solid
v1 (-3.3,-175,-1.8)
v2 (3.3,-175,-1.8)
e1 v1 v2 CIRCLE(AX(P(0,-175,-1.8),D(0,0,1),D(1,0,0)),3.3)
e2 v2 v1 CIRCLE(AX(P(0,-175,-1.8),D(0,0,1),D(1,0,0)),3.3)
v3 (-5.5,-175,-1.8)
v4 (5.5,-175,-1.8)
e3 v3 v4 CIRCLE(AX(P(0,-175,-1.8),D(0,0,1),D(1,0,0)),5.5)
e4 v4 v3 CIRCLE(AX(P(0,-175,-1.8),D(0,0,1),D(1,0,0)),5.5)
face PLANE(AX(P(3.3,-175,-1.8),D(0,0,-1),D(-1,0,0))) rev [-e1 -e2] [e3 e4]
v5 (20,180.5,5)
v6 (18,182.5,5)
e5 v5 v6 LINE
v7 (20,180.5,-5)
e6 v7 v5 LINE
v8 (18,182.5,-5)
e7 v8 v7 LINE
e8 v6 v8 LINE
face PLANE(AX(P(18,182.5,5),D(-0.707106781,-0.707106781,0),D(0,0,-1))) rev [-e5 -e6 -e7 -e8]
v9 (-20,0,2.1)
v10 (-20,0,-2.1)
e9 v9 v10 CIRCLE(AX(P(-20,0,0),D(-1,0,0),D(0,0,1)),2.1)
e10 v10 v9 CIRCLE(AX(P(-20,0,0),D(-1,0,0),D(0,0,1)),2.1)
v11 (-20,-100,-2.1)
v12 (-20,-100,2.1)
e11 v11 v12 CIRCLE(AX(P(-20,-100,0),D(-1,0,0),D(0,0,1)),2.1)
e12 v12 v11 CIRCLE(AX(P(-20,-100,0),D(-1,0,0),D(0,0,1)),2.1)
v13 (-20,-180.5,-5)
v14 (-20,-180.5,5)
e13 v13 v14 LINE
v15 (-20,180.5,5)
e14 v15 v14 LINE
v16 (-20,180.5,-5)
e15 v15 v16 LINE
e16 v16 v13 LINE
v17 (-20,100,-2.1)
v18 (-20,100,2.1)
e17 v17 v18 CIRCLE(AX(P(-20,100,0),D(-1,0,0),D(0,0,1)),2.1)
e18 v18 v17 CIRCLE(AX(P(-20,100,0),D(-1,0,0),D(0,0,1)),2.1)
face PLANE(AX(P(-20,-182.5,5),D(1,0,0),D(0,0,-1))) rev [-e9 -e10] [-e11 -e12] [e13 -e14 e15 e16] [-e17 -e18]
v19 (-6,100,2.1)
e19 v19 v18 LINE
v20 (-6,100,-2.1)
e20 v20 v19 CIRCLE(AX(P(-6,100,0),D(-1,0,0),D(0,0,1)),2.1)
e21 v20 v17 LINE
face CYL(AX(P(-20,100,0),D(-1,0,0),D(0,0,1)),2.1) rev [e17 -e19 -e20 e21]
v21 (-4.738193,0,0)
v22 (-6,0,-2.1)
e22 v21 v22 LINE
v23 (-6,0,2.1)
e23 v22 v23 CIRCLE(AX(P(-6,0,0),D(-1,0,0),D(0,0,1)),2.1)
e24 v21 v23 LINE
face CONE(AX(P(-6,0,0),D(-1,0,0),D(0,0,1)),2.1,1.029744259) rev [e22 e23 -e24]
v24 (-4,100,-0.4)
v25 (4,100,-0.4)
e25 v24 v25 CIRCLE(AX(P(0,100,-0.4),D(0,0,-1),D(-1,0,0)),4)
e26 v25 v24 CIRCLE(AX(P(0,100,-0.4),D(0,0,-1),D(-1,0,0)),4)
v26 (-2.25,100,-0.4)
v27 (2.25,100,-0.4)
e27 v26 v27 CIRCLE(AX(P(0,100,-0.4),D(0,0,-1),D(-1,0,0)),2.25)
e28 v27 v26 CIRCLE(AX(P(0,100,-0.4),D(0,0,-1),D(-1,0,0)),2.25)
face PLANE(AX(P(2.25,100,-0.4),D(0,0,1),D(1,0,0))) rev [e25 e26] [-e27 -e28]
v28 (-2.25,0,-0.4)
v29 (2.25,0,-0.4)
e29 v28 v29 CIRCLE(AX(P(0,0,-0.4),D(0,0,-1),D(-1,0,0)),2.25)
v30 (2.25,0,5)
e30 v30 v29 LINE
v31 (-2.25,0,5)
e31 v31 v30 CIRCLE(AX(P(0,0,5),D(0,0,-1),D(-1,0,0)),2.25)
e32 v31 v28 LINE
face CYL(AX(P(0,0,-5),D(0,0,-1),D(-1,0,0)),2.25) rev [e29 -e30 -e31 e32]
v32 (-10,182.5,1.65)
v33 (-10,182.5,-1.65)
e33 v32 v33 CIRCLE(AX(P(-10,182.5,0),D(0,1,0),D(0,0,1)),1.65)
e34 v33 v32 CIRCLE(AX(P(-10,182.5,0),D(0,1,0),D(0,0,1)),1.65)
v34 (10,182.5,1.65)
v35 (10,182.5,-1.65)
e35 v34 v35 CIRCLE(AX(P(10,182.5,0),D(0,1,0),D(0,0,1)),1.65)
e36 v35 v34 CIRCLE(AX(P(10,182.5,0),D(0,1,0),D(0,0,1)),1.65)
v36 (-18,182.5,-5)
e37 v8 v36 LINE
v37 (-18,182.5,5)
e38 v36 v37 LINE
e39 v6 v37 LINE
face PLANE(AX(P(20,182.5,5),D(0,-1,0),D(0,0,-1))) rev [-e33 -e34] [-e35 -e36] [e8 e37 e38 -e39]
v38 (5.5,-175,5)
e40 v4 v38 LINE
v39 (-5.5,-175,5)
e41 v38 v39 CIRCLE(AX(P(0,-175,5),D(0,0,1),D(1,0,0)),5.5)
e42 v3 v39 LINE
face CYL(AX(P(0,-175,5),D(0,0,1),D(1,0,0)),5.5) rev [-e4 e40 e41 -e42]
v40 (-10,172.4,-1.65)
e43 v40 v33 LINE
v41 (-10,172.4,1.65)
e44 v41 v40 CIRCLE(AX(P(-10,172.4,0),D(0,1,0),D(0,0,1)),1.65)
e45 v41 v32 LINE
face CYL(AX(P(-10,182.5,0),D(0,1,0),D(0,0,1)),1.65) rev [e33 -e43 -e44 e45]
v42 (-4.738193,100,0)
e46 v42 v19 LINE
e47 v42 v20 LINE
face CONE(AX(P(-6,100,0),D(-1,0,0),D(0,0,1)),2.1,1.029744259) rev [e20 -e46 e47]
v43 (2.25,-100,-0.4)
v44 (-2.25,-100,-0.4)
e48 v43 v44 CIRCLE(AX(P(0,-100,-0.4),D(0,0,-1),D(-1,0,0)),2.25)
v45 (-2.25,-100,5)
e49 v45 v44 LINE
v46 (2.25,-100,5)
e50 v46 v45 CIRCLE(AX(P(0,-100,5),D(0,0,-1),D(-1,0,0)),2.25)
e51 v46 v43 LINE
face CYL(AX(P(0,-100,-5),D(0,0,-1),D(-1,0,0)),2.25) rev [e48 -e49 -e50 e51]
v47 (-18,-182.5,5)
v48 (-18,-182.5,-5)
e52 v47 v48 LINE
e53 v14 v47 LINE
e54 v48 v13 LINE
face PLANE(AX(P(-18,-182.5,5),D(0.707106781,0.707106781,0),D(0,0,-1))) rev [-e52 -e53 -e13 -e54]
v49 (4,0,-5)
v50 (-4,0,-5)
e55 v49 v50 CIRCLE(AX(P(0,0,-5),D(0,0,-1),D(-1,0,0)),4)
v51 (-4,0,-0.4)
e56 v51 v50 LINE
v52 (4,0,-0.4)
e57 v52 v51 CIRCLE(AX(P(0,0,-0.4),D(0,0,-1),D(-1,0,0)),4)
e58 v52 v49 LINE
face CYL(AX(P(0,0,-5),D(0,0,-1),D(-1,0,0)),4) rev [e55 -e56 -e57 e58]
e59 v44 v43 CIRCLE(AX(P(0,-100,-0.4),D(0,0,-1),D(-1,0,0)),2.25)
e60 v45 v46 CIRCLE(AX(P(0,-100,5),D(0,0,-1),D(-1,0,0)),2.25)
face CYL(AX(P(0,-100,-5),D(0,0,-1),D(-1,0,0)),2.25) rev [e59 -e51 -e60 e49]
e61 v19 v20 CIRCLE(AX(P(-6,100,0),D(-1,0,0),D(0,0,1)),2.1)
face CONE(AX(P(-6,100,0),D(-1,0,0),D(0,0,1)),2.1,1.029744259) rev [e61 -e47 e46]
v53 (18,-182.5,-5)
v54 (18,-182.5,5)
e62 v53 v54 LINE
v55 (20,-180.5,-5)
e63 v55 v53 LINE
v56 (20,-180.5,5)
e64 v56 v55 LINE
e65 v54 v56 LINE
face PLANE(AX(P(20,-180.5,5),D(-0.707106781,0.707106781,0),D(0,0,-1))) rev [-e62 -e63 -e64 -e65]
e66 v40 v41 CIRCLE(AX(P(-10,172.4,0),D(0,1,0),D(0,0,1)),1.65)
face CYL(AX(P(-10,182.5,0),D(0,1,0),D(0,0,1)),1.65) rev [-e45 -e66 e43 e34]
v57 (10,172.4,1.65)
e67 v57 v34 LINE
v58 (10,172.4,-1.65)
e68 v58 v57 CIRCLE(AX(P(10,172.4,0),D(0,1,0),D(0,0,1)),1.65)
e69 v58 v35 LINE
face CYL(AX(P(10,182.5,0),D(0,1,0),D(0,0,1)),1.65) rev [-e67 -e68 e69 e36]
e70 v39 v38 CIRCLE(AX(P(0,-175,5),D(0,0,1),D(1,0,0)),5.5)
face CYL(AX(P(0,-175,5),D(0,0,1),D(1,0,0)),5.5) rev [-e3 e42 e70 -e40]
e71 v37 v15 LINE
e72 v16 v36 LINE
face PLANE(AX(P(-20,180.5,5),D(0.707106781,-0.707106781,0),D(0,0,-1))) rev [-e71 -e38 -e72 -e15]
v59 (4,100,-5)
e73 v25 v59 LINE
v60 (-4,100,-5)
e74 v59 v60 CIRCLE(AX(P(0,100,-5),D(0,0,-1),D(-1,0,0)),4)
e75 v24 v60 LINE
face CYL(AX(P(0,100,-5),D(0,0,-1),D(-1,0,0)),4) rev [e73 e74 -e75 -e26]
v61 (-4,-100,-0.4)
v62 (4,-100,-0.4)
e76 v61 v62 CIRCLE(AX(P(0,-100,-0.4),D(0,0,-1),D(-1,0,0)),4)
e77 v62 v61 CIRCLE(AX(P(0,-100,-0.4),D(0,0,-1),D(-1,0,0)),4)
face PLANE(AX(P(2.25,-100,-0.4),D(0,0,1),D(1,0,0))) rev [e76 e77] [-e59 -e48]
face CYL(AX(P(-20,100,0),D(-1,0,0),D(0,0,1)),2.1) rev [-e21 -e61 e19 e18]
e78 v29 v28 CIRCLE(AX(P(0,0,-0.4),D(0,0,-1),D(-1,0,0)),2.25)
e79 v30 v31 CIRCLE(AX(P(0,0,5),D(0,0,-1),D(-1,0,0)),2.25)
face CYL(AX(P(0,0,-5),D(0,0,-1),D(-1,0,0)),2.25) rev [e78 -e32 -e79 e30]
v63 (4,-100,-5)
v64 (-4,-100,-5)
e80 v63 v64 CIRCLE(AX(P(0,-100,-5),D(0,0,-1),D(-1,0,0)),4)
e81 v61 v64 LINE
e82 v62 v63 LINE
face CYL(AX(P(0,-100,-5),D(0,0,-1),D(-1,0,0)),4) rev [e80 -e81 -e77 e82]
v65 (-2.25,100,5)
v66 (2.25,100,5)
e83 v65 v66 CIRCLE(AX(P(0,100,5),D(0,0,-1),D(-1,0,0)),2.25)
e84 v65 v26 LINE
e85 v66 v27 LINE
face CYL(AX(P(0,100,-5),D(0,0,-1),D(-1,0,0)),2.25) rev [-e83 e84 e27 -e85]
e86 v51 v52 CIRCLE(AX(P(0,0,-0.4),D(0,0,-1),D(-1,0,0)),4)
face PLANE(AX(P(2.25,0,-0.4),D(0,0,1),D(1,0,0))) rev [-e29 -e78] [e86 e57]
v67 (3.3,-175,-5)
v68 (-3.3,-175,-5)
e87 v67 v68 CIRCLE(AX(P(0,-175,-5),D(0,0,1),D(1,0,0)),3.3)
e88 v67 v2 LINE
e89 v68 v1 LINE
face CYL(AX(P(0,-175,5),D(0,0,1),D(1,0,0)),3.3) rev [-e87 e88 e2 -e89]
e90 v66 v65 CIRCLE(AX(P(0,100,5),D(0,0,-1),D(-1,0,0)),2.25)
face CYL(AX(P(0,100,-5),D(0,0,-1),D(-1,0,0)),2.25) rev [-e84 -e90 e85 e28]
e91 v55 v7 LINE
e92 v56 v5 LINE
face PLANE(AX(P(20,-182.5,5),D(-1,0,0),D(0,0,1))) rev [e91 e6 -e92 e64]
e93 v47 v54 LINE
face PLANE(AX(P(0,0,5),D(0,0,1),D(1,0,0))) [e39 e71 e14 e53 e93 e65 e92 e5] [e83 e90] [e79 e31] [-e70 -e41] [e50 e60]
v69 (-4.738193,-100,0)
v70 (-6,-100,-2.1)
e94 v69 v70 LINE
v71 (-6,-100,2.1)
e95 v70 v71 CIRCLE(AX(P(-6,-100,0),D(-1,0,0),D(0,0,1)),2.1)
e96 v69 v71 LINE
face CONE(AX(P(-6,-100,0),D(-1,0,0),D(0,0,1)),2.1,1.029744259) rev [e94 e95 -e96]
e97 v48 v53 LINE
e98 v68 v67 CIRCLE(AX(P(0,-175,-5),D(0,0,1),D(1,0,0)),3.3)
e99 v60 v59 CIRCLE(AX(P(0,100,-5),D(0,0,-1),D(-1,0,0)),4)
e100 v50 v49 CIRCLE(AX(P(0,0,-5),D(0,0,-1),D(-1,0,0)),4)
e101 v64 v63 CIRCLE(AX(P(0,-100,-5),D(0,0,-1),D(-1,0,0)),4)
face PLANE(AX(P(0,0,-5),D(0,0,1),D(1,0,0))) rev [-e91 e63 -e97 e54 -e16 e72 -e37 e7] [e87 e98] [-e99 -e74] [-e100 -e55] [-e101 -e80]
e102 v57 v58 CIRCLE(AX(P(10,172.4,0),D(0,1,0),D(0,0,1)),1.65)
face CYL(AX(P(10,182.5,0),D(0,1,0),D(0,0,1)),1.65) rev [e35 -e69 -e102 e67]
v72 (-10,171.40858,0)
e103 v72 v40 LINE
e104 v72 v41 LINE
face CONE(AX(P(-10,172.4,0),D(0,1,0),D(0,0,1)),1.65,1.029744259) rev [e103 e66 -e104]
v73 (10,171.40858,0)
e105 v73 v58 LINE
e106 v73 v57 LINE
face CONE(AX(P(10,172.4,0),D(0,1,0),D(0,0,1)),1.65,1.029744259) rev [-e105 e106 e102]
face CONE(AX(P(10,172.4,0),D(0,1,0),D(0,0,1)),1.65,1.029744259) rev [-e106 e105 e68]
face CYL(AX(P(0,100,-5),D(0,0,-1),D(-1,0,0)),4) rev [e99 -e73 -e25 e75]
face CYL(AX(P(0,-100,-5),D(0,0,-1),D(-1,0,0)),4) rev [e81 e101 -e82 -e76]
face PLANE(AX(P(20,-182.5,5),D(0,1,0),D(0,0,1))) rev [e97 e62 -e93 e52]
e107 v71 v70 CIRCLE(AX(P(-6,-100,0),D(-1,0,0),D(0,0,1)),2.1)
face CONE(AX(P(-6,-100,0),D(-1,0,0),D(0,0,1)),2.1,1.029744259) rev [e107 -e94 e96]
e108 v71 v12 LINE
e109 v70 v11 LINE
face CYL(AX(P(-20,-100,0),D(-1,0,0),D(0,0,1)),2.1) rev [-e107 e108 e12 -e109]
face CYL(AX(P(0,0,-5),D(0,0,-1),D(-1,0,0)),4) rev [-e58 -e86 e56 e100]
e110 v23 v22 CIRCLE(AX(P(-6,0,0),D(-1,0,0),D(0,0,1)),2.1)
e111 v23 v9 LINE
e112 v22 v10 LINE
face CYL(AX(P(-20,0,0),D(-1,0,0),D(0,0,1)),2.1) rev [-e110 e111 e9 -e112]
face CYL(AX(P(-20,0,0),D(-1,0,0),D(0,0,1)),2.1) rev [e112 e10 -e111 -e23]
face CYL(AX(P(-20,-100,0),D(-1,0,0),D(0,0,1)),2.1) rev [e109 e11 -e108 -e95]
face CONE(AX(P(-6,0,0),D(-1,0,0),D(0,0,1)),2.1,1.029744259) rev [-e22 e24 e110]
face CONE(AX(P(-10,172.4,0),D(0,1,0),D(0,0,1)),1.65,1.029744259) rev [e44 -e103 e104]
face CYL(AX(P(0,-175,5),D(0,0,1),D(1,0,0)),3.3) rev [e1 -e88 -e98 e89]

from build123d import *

# Parameters (mm, degrees)
SKETCH1_W                                    = 40
SKETCH1_H                                    = 365
BOSS_EXTRUDE1_DEPTH                          = 5
M4_TAPPED_HOLE2_D                            = 3.3
M4_TAPPED_HOLE2_DEPTH                        = 10.1
M4_TAPPED_HOLE2_TIP                          = 0.991420021
HEX_SOCKET_CAP_SCREW_HOLE_TYPE_1_D           = 6.6
HEX_SOCKET_CAP_SCREW_HOLE_TYPE_1_CBORE_D     = 11
HEX_SOCKET_CAP_SCREW_HOLE_TYPE_1_CBORE_DEPTH = 6.8
M5_TAPPED_HOLE1_D                            = 4.2
M5_TAPPED_HOLE1_DEPTH                        = 14
M5_TAPPED_HOLE1_TIP                          = 1.2618073
CHAMFER1_SIZE                                = 2
HEX_SOCKET_CAP_SCREW_HOLE_TYPE_2_D           = 4.5
HEX_SOCKET_CAP_SCREW_HOLE_TYPE_2_CBORE_D     = 8
HEX_SOCKET_CAP_SCREW_HOLE_TYPE_2_CBORE_DEPTH = 4.6


with BuildPart() as part:
    # Sketch1 → Boss-Extrude1 (new, symmetric)
    with BuildSketch(Plane.XY):
        Rectangle(SKETCH1_W, SKETCH1_H)
    extrude(amount=BOSS_EXTRUDE1_DEPTH, both=True)

    # M4 Tapped Hole2
    with Locations(Plane(origin=(0, 182.5, 0), x_dir=(1, 0, 0), z_dir=(0, 1, 0))):
        with Locations((10, 0), (-10, 0)):
            Hole(M4_TAPPED_HOLE2_D / 2, depth=M4_TAPPED_HOLE2_DEPTH)
            with Locations((0, 0, -(M4_TAPPED_HOLE2_DEPTH + M4_TAPPED_HOLE2_TIP / 2))):  # 118° drill point
                Cone(0, M4_TAPPED_HOLE2_D / 2, M4_TAPPED_HOLE2_TIP, mode=Mode.SUBTRACT)

    # Hex socket cap screw hole type 1 (through all)
    with Locations(Plane.XY.offset(5)):
        with Locations((0, -175)):
            CounterBoreHole(HEX_SOCKET_CAP_SCREW_HOLE_TYPE_1_D / 2, HEX_SOCKET_CAP_SCREW_HOLE_TYPE_1_CBORE_D / 2, HEX_SOCKET_CAP_SCREW_HOLE_TYPE_1_CBORE_DEPTH)

    # M5 Tapped Hole1
    with Locations(Plane.ZY.offset(20)):
        with Locations((0, 0), (0, 100), (0, -100)):
            Hole(M5_TAPPED_HOLE1_D / 2, depth=M5_TAPPED_HOLE1_DEPTH)
            with Locations((0, 0, -(M5_TAPPED_HOLE1_DEPTH + M5_TAPPED_HOLE1_TIP / 2))):  # 118° drill point
                Cone(0, M5_TAPPED_HOLE1_D / 2, M5_TAPPED_HOLE1_TIP, mode=Mode.SUBTRACT)

    # Chamfer1
    chamfer1_edges = [part.edges().sort_by_distance(p)[0] for p in [
        (-20, 182.5, 0),
        (20, 182.5, 0),
        (20, -182.5, 0),
        (-20, -182.5, 0),
    ]]
    chamfer(chamfer1_edges, length=CHAMFER1_SIZE)

    # Hex socket cap screw hole type 2 (through all)
    with Locations(Plane(origin=(0, 0, -5), x_dir=(-1, 0, 0), z_dir=(0, 0, -1))):
        with Locations((0, 100), (0, 0), (0, -100)):
            CounterBoreHole(HEX_SOCKET_CAP_SCREW_HOLE_TYPE_2_D / 2, HEX_SOCKET_CAP_SCREW_HOLE_TYPE_2_CBORE_D / 2, HEX_SOCKET_CAP_SCREW_HOLE_TYPE_2_CBORE_DEPTH)


solid = part.part
